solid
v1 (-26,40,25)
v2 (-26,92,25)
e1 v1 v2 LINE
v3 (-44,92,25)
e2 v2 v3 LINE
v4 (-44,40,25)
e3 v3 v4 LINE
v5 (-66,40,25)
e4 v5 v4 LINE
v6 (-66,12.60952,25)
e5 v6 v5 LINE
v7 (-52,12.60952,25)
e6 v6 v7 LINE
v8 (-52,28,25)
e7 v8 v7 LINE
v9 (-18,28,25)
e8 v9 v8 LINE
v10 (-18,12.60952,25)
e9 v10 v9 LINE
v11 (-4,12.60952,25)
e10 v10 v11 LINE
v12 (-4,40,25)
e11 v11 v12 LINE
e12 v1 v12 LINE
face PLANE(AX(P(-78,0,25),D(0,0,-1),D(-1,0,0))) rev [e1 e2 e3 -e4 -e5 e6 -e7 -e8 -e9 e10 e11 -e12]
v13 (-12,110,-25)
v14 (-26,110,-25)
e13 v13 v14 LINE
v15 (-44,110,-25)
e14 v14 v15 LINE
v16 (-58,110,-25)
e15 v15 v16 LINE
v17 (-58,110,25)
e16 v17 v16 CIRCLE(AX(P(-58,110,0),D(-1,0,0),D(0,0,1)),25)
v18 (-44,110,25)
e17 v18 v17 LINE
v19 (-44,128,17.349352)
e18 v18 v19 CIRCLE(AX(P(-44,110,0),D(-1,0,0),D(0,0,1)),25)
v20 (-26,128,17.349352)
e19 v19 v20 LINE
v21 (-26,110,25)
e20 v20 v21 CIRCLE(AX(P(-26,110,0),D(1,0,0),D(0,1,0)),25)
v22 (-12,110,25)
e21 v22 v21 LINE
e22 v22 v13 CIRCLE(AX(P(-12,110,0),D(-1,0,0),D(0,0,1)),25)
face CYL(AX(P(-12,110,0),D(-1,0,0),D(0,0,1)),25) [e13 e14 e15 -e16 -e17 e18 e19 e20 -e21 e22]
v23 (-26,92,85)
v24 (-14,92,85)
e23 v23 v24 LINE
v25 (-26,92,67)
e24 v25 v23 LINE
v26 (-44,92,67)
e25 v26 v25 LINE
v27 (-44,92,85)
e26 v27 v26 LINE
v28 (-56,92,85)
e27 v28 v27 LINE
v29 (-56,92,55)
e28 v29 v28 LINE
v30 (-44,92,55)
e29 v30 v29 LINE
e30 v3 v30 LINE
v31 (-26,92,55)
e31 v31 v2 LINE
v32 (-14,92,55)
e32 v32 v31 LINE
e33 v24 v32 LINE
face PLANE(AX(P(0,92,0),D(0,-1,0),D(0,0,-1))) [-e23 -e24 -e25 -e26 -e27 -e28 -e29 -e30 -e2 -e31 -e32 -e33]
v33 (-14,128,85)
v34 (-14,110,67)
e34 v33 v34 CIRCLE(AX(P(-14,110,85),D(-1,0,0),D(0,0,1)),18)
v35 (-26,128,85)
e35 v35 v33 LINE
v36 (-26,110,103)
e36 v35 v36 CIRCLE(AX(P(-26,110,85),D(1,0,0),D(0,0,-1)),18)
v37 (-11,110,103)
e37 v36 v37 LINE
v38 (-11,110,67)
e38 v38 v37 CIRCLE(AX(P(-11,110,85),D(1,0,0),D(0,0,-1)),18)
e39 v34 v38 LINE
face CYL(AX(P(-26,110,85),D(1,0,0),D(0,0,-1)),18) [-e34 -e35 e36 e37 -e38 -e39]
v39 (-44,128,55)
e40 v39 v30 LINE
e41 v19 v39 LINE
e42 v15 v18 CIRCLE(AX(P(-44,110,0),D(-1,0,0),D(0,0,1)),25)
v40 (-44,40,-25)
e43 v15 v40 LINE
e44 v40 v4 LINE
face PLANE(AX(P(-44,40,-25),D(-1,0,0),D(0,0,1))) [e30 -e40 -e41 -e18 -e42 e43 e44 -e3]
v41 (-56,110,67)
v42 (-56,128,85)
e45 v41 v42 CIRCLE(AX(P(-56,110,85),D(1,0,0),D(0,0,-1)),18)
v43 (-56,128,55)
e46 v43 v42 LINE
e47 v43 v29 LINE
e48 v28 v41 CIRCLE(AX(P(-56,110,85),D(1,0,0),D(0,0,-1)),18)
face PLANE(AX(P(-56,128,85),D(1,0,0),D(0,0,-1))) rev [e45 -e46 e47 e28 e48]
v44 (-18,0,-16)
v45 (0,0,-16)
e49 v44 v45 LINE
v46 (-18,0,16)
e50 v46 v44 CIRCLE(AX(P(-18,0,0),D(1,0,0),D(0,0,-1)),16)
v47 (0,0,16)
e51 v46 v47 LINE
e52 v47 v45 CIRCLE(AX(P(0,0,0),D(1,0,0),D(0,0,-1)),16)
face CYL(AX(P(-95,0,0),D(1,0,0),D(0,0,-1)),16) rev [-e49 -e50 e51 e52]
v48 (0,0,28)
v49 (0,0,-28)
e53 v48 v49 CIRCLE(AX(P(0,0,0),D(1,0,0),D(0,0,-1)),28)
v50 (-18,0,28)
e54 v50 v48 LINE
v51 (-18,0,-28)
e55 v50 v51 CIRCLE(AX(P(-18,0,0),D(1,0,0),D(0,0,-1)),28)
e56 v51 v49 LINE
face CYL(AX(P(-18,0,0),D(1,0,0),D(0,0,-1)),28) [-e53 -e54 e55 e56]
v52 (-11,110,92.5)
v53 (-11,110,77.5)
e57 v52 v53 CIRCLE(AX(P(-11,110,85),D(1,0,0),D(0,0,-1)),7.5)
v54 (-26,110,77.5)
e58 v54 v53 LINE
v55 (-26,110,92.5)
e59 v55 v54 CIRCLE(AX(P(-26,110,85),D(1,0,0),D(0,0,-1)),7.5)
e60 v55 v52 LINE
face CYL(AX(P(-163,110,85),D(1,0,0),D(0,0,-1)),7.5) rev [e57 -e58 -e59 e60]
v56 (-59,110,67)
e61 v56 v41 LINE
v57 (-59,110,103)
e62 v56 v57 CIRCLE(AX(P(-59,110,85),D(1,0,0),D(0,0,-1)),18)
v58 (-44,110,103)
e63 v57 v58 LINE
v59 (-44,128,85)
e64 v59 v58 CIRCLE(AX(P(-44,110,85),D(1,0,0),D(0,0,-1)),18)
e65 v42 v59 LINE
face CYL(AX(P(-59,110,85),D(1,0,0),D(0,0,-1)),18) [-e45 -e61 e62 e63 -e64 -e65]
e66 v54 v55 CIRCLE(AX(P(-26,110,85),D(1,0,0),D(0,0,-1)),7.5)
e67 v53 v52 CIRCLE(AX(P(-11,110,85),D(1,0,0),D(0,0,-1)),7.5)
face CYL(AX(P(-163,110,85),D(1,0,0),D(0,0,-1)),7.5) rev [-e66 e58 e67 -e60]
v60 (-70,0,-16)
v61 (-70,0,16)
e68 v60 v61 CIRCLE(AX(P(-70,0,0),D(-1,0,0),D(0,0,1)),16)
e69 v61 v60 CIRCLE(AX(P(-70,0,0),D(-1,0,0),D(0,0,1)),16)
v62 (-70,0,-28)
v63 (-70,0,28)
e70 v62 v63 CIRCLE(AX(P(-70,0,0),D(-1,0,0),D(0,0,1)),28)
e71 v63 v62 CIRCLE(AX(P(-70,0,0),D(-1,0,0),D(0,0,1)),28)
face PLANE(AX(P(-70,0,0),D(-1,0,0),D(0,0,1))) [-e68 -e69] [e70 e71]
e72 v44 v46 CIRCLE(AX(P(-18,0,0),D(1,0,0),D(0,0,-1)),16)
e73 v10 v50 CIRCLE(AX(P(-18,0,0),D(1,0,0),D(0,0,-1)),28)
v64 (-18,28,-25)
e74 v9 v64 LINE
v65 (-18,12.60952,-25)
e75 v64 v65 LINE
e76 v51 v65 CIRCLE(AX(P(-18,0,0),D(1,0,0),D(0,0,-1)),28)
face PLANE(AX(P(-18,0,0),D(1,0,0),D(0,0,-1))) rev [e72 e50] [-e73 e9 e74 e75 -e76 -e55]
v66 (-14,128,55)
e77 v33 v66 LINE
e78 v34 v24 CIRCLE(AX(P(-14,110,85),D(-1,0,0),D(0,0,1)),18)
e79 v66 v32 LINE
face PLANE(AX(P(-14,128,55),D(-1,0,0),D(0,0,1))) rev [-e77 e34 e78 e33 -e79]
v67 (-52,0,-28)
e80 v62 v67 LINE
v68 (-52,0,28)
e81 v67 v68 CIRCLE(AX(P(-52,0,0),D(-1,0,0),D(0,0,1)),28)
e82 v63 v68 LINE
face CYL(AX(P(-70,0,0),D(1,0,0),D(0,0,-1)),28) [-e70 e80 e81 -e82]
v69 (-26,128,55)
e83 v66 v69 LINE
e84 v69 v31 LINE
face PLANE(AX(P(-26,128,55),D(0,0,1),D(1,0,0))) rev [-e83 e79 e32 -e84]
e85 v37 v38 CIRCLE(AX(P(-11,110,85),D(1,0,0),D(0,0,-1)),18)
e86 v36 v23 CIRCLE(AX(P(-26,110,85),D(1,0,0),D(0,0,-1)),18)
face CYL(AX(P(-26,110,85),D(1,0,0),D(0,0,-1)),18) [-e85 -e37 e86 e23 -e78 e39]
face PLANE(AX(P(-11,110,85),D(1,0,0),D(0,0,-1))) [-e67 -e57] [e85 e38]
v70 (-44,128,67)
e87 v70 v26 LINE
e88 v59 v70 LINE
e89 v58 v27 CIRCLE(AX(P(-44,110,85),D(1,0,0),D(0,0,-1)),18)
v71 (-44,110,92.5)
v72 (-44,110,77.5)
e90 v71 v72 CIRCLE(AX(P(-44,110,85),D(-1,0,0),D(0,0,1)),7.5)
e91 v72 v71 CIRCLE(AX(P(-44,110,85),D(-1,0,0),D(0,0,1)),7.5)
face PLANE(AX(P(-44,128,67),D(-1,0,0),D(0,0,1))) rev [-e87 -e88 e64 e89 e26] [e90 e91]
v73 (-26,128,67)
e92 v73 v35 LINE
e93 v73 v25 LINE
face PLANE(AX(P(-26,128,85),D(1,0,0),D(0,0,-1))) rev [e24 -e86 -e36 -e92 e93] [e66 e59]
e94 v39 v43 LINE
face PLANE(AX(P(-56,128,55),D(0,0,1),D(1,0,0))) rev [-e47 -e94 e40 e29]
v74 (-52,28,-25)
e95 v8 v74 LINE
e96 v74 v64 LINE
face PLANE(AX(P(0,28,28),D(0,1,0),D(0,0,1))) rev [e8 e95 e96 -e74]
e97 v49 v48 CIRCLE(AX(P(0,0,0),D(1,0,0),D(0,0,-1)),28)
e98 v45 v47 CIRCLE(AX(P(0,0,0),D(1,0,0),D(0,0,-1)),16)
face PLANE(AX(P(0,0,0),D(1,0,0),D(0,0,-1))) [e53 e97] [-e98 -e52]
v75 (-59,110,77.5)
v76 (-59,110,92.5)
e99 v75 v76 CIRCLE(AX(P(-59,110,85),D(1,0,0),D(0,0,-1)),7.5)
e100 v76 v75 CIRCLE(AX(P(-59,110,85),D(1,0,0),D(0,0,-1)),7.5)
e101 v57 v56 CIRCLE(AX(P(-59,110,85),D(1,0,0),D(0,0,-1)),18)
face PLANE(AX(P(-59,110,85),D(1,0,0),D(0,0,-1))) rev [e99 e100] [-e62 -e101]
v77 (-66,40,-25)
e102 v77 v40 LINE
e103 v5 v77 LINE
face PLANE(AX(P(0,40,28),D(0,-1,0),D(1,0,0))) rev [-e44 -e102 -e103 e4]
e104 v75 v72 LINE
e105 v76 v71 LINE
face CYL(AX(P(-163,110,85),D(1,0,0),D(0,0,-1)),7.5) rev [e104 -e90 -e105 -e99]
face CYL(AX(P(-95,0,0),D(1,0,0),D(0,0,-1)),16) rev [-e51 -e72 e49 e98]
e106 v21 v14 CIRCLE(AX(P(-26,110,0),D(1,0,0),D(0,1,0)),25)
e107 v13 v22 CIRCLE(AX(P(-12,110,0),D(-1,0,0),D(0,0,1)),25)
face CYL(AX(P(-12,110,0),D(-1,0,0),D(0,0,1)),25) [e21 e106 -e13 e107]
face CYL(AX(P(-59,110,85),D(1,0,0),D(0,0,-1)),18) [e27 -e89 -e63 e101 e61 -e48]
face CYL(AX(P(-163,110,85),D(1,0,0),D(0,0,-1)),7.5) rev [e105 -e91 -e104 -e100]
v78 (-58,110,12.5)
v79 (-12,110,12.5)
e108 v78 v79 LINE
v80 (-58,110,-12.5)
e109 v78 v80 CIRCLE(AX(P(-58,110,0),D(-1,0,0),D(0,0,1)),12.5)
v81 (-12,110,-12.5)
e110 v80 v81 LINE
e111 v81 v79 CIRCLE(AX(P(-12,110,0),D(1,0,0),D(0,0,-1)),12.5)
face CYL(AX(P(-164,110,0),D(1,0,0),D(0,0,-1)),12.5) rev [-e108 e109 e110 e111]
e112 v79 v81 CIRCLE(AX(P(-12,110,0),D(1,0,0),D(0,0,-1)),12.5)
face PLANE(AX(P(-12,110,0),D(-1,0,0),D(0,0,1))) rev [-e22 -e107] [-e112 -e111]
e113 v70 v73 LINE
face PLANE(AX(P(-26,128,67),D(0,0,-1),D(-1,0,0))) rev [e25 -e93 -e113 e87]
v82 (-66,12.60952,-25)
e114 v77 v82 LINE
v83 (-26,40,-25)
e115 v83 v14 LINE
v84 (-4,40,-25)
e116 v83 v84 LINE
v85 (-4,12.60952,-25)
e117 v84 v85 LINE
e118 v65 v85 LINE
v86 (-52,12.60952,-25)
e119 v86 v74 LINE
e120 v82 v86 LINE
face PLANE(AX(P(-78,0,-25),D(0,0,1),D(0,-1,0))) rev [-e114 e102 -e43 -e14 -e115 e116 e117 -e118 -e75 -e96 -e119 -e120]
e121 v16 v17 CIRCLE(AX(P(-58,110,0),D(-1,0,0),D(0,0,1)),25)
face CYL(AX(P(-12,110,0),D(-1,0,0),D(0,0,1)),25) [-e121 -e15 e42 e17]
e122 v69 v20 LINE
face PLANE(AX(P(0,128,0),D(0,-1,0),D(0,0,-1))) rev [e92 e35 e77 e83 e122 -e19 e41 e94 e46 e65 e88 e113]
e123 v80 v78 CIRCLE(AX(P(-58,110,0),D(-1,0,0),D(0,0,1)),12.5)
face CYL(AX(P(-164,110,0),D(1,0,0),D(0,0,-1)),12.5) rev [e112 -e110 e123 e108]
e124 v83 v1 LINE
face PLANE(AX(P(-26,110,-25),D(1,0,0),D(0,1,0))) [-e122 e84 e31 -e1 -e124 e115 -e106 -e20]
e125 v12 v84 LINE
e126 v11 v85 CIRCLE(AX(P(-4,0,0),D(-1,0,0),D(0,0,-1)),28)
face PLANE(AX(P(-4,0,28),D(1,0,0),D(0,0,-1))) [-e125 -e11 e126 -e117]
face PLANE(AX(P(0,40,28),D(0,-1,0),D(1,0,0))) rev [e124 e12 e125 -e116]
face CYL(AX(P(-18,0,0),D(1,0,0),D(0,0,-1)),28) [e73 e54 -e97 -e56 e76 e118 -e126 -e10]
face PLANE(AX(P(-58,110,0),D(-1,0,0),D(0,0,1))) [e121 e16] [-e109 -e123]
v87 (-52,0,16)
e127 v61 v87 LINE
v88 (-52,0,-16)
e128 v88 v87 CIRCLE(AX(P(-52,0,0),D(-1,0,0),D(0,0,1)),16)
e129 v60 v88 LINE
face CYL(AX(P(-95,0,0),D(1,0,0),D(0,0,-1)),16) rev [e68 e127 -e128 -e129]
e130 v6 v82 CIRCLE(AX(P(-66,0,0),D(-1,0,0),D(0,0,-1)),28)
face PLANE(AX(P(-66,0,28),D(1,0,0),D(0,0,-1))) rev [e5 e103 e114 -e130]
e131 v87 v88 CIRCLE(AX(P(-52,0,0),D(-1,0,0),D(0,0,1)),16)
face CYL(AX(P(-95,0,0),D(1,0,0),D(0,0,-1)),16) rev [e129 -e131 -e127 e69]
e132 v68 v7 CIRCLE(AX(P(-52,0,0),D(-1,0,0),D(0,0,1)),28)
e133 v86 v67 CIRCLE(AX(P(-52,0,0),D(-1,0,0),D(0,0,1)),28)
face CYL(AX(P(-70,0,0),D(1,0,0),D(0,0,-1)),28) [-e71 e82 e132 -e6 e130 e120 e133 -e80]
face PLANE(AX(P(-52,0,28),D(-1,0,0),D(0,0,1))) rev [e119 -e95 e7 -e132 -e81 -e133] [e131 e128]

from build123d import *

# Parameters (mm, degrees)
CLEVIS_EYE_A_SKETCH_R        = 28
CLEVIS_EYE_A_56_DEPTH        = 18
CLEVIS_EYE_B_SKETCH_R        = 28
CLEVIS_EYE_B_56_DEPTH        = 18
CLEVIS_BORE_SKETCH_R         = 16
CLEVIS_BORE_DEPTH            = 95
LINK_WEB_DEPTH               = 28
WEB_GUSSET_1_DEPTH           = 14
WEB_START                    = -14
WEB_GUSSET_2_DEPTH           = 14
WEB_SLOT_CUT_DEPTH           = 74
LOWER_FORK_BLOCK_SKETCH_W    = 18
LOWER_FORK_BLOCK_SKETCH_H    = 70
LOWER_FORK_BLOCK_DEPTH       = 50
LOWER_FORK_EYE_DEPTH         = 14
LOWER_FORK_EYE_DEPTH_BACK    = 32
LOWER_FORK_EYE_SKETCH_R      = 25
UPPER_FORK_PROFILE_DEPTH     = 18
UPPER_FORK_EYE_36_DEPTH      = 3
UPPER_FORK_EYE_36_DEPTH_BACK = 12
UPPER_FORK_EYE_SKETCH_36_R   = 18
UPPER_FORK_HUB_SKETCH_R      = 18
UPPER_FORK_HUB_DEPTH         = 15
UPPER_FORK_PIN_BORE_SKETCH_R = 7.5
UPPER_FORK_PIN_BORE_DEPTH    = 152
LOWER_FORK_PIN_BORE_SKETCH_R = 12.5
LOWER_FORK_PIN_BORE_DEPTH    = 152


with BuildPart() as part:
    # Clevis Eye A Sketch → Clevis Eye A Ø56 (new body)
    with BuildSketch(Plane(origin=(0, 0, 0), x_dir=(0, 0, -1), z_dir=(1, 0, 0))):
        Circle(CLEVIS_EYE_A_SKETCH_R)
    extrude(amount=-CLEVIS_EYE_A_56_DEPTH)


with BuildPart() as body_2:
    # Clevis Eye B Sketch → Clevis Eye B Ø56 (new body)
    with BuildSketch(Plane.ZY.offset(52)):
        with Locations(Location((0, 0, 0), (0, 0, 180))):
            Circle(CLEVIS_EYE_B_SKETCH_R)
    extrude(amount=CLEVIS_EYE_B_56_DEPTH)


with BuildPart() as clevis_bore_tool:
    # Clevis Bore Sketch → Clevis Bore (new body)
    with BuildSketch(Plane(origin=(0, 0, 0), x_dir=(0, 0, -1), z_dir=(1, 0, 0))):
        Circle(CLEVIS_BORE_SKETCH_R)
    extrude(amount=-CLEVIS_BORE_DEPTH)


with BuildPart() as part_1:
    add(part.part)

    # Clevis Bore: cut by clevis_bore_tool
    add(clevis_bore_tool.part, mode=Mode.SUBTRACT)



with BuildPart() as body_2_1:
    add(body_2.part)

    # Clevis Bore: cut by clevis_bore_tool
    add(clevis_bore_tool.part, mode=Mode.SUBTRACT)


with BuildPart() as part_2:
    add(part_1.part)

    add(body_2_1.part)  # Link Web merges body 2
    # Link Web Sketch → Link Web (add, symmetric)
    with BuildSketch(Plane.XY):
        Polygon((-66, 40), (-66, 16), (-52, 16), (-52, 26), (-52, 28), (-18, 28), (-18, 26), (-18, 16), (-4, 16), (-4, 40), align=None)
    extrude(amount=LINK_WEB_DEPTH, both=True)

    # Web Gusset 1 Sketch → Web Gusset 1 (add)
    with BuildSketch(Plane(origin=(-4, 0, 0), x_dir=(0, 0, -1), z_dir=(1, 0, 0))):
        with BuildLine():
            Line((-28, 16), (-28, 0))
            ThreePointArc((-28, 0), (-26.71508, 8.384777), (-22.978251, 16))
            Line((-22.978251, 16), (-28, 16))
        make_face()
        with BuildLine():
            Line((28, 16), (28, 0))
            ThreePointArc((28, 0), (26.71508, 8.384777), (22.978251, 16))
            Line((22.978251, 16), (28, 16))
        make_face()
    extrude(amount=-WEB_GUSSET_1_DEPTH)

    # Web Gusset 2 Sketch → Web Gusset 2 (add)
    with BuildSketch(Plane.ZY.offset(66).offset(WEB_START)):
        with BuildLine():
            Line((28, 16), (28, 0))
            ThreePointArc((28, 0), (26.71508, 8.384777), (22.978251, 16))
            Line((22.978251, 16), (28, 16))
        make_face()
        with BuildLine():
            Line((-28, 0), (-28, 16))
            Line((-28, 16), (-22.978251, 16))
            ThreePointArc((-22.978251, 16), (-26.71508, 8.384777), (-28, 0))
        make_face()
    extrude(amount=WEB_GUSSET_2_DEPTH)

    # Web Slot Sketch → Web Slot Cut (cut)
    with BuildSketch(Plane(origin=(-4, 0, 0), x_dir=(0, 0, -1), z_dir=(1, 0, 0))):
        with BuildLine():
            Line((-25, 12.60952), (-25, 40))
            Line((-25, 40), (-28, 40))
            Line((-28, 40), (-28, 0))
            ThreePointArc((-28, 0), (-27.239677, 6.480741), (-25, 12.60952))
        make_face()
        with BuildLine():
            Line((28, 40), (25, 40))
            Line((25, 40), (25, 12.60952))
            ThreePointArc((25, 12.60952), (27.239677, 6.480741), (28, 0))
            Line((28, 0), (28, 40))
        make_face()
    extrude(amount=-WEB_SLOT_CUT_DEPTH, mode=Mode.SUBTRACT)

    # Lower Fork Block Sketch → Lower Fork Block (add)
    with BuildSketch(Plane.XY.offset(25)):
        with Locations((-35, 75)):
            Rectangle(LOWER_FORK_BLOCK_SKETCH_W, LOWER_FORK_BLOCK_SKETCH_H)
    extrude(amount=-LOWER_FORK_BLOCK_DEPTH)

    # Lower Fork Eye Sketch → Lower Fork Eye (add, two sides: drawn at the far end of the back side and taken through both)
    with BuildSketch(Plane.ZY.offset(44).offset(-LOWER_FORK_EYE_DEPTH_BACK)):
        with Locations((0, 110)):
            Circle(LOWER_FORK_EYE_SKETCH_R)
    extrude(amount=LOWER_FORK_EYE_DEPTH + LOWER_FORK_EYE_DEPTH_BACK)

    # Upper Fork Profile Sketch → Upper Fork Profile (add, symmetric)
    with BuildSketch(Plane(origin=(0, 110, 0), x_dir=(1, 0, 0), z_dir=(0, 1, 0))):
        Polygon((-26, -55), (-14, -55), (-14, -85), (-26, -85), (-26, -67), (-44, -67), (-44, -85), (-56, -85), (-56, -55), (-44, -55), (-44, 0), (-26, 0), align=None)
    extrude(amount=UPPER_FORK_PROFILE_DEPTH, both=True)

    # Upper Fork Eye Sketch Ø36 → Upper Fork Eye Ø36 (add, two sides: drawn at the far end of the back side and taken through both)
    with BuildSketch(Plane(origin=(-14, 0, 0), x_dir=(0, 0, -1), z_dir=(1, 0, 0)).offset(-UPPER_FORK_EYE_36_DEPTH_BACK)):
        with Locations((-85, 110)):
            Circle(UPPER_FORK_EYE_SKETCH_36_R)
    extrude(amount=UPPER_FORK_EYE_36_DEPTH + UPPER_FORK_EYE_36_DEPTH_BACK)

    # Upper Fork Hub Sketch → Upper Fork Hub (add)
    with BuildSketch(Plane(origin=(-44, 0, 0), x_dir=(0, 0, -1), z_dir=(1, 0, 0))):
        with Locations((-85, 110)):
            Circle(UPPER_FORK_HUB_SKETCH_R)
    extrude(amount=-UPPER_FORK_HUB_DEPTH)

    # Upper Fork Pin Bore Sketch → Upper Fork Pin Bore (cut)
    with BuildSketch(Plane(origin=(-11, 0, 0), x_dir=(0, 0, -1), z_dir=(1, 0, 0))):
        with Locations((-85, 110)):
            Circle(UPPER_FORK_PIN_BORE_SKETCH_R)
    extrude(amount=-UPPER_FORK_PIN_BORE_DEPTH, mode=Mode.SUBTRACT)

    # Lower Fork Pin Bore Sketch → Lower Fork Pin Bore (cut)
    with BuildSketch(Plane(origin=(-12, 0, 0), x_dir=(0, 0, -1), z_dir=(1, 0, 0))):
        with Locations((0, 110)):
            Circle(LOWER_FORK_PIN_BORE_SKETCH_R)
    extrude(amount=-LOWER_FORK_PIN_BORE_DEPTH, mode=Mode.SUBTRACT)


solid = part_2.part
